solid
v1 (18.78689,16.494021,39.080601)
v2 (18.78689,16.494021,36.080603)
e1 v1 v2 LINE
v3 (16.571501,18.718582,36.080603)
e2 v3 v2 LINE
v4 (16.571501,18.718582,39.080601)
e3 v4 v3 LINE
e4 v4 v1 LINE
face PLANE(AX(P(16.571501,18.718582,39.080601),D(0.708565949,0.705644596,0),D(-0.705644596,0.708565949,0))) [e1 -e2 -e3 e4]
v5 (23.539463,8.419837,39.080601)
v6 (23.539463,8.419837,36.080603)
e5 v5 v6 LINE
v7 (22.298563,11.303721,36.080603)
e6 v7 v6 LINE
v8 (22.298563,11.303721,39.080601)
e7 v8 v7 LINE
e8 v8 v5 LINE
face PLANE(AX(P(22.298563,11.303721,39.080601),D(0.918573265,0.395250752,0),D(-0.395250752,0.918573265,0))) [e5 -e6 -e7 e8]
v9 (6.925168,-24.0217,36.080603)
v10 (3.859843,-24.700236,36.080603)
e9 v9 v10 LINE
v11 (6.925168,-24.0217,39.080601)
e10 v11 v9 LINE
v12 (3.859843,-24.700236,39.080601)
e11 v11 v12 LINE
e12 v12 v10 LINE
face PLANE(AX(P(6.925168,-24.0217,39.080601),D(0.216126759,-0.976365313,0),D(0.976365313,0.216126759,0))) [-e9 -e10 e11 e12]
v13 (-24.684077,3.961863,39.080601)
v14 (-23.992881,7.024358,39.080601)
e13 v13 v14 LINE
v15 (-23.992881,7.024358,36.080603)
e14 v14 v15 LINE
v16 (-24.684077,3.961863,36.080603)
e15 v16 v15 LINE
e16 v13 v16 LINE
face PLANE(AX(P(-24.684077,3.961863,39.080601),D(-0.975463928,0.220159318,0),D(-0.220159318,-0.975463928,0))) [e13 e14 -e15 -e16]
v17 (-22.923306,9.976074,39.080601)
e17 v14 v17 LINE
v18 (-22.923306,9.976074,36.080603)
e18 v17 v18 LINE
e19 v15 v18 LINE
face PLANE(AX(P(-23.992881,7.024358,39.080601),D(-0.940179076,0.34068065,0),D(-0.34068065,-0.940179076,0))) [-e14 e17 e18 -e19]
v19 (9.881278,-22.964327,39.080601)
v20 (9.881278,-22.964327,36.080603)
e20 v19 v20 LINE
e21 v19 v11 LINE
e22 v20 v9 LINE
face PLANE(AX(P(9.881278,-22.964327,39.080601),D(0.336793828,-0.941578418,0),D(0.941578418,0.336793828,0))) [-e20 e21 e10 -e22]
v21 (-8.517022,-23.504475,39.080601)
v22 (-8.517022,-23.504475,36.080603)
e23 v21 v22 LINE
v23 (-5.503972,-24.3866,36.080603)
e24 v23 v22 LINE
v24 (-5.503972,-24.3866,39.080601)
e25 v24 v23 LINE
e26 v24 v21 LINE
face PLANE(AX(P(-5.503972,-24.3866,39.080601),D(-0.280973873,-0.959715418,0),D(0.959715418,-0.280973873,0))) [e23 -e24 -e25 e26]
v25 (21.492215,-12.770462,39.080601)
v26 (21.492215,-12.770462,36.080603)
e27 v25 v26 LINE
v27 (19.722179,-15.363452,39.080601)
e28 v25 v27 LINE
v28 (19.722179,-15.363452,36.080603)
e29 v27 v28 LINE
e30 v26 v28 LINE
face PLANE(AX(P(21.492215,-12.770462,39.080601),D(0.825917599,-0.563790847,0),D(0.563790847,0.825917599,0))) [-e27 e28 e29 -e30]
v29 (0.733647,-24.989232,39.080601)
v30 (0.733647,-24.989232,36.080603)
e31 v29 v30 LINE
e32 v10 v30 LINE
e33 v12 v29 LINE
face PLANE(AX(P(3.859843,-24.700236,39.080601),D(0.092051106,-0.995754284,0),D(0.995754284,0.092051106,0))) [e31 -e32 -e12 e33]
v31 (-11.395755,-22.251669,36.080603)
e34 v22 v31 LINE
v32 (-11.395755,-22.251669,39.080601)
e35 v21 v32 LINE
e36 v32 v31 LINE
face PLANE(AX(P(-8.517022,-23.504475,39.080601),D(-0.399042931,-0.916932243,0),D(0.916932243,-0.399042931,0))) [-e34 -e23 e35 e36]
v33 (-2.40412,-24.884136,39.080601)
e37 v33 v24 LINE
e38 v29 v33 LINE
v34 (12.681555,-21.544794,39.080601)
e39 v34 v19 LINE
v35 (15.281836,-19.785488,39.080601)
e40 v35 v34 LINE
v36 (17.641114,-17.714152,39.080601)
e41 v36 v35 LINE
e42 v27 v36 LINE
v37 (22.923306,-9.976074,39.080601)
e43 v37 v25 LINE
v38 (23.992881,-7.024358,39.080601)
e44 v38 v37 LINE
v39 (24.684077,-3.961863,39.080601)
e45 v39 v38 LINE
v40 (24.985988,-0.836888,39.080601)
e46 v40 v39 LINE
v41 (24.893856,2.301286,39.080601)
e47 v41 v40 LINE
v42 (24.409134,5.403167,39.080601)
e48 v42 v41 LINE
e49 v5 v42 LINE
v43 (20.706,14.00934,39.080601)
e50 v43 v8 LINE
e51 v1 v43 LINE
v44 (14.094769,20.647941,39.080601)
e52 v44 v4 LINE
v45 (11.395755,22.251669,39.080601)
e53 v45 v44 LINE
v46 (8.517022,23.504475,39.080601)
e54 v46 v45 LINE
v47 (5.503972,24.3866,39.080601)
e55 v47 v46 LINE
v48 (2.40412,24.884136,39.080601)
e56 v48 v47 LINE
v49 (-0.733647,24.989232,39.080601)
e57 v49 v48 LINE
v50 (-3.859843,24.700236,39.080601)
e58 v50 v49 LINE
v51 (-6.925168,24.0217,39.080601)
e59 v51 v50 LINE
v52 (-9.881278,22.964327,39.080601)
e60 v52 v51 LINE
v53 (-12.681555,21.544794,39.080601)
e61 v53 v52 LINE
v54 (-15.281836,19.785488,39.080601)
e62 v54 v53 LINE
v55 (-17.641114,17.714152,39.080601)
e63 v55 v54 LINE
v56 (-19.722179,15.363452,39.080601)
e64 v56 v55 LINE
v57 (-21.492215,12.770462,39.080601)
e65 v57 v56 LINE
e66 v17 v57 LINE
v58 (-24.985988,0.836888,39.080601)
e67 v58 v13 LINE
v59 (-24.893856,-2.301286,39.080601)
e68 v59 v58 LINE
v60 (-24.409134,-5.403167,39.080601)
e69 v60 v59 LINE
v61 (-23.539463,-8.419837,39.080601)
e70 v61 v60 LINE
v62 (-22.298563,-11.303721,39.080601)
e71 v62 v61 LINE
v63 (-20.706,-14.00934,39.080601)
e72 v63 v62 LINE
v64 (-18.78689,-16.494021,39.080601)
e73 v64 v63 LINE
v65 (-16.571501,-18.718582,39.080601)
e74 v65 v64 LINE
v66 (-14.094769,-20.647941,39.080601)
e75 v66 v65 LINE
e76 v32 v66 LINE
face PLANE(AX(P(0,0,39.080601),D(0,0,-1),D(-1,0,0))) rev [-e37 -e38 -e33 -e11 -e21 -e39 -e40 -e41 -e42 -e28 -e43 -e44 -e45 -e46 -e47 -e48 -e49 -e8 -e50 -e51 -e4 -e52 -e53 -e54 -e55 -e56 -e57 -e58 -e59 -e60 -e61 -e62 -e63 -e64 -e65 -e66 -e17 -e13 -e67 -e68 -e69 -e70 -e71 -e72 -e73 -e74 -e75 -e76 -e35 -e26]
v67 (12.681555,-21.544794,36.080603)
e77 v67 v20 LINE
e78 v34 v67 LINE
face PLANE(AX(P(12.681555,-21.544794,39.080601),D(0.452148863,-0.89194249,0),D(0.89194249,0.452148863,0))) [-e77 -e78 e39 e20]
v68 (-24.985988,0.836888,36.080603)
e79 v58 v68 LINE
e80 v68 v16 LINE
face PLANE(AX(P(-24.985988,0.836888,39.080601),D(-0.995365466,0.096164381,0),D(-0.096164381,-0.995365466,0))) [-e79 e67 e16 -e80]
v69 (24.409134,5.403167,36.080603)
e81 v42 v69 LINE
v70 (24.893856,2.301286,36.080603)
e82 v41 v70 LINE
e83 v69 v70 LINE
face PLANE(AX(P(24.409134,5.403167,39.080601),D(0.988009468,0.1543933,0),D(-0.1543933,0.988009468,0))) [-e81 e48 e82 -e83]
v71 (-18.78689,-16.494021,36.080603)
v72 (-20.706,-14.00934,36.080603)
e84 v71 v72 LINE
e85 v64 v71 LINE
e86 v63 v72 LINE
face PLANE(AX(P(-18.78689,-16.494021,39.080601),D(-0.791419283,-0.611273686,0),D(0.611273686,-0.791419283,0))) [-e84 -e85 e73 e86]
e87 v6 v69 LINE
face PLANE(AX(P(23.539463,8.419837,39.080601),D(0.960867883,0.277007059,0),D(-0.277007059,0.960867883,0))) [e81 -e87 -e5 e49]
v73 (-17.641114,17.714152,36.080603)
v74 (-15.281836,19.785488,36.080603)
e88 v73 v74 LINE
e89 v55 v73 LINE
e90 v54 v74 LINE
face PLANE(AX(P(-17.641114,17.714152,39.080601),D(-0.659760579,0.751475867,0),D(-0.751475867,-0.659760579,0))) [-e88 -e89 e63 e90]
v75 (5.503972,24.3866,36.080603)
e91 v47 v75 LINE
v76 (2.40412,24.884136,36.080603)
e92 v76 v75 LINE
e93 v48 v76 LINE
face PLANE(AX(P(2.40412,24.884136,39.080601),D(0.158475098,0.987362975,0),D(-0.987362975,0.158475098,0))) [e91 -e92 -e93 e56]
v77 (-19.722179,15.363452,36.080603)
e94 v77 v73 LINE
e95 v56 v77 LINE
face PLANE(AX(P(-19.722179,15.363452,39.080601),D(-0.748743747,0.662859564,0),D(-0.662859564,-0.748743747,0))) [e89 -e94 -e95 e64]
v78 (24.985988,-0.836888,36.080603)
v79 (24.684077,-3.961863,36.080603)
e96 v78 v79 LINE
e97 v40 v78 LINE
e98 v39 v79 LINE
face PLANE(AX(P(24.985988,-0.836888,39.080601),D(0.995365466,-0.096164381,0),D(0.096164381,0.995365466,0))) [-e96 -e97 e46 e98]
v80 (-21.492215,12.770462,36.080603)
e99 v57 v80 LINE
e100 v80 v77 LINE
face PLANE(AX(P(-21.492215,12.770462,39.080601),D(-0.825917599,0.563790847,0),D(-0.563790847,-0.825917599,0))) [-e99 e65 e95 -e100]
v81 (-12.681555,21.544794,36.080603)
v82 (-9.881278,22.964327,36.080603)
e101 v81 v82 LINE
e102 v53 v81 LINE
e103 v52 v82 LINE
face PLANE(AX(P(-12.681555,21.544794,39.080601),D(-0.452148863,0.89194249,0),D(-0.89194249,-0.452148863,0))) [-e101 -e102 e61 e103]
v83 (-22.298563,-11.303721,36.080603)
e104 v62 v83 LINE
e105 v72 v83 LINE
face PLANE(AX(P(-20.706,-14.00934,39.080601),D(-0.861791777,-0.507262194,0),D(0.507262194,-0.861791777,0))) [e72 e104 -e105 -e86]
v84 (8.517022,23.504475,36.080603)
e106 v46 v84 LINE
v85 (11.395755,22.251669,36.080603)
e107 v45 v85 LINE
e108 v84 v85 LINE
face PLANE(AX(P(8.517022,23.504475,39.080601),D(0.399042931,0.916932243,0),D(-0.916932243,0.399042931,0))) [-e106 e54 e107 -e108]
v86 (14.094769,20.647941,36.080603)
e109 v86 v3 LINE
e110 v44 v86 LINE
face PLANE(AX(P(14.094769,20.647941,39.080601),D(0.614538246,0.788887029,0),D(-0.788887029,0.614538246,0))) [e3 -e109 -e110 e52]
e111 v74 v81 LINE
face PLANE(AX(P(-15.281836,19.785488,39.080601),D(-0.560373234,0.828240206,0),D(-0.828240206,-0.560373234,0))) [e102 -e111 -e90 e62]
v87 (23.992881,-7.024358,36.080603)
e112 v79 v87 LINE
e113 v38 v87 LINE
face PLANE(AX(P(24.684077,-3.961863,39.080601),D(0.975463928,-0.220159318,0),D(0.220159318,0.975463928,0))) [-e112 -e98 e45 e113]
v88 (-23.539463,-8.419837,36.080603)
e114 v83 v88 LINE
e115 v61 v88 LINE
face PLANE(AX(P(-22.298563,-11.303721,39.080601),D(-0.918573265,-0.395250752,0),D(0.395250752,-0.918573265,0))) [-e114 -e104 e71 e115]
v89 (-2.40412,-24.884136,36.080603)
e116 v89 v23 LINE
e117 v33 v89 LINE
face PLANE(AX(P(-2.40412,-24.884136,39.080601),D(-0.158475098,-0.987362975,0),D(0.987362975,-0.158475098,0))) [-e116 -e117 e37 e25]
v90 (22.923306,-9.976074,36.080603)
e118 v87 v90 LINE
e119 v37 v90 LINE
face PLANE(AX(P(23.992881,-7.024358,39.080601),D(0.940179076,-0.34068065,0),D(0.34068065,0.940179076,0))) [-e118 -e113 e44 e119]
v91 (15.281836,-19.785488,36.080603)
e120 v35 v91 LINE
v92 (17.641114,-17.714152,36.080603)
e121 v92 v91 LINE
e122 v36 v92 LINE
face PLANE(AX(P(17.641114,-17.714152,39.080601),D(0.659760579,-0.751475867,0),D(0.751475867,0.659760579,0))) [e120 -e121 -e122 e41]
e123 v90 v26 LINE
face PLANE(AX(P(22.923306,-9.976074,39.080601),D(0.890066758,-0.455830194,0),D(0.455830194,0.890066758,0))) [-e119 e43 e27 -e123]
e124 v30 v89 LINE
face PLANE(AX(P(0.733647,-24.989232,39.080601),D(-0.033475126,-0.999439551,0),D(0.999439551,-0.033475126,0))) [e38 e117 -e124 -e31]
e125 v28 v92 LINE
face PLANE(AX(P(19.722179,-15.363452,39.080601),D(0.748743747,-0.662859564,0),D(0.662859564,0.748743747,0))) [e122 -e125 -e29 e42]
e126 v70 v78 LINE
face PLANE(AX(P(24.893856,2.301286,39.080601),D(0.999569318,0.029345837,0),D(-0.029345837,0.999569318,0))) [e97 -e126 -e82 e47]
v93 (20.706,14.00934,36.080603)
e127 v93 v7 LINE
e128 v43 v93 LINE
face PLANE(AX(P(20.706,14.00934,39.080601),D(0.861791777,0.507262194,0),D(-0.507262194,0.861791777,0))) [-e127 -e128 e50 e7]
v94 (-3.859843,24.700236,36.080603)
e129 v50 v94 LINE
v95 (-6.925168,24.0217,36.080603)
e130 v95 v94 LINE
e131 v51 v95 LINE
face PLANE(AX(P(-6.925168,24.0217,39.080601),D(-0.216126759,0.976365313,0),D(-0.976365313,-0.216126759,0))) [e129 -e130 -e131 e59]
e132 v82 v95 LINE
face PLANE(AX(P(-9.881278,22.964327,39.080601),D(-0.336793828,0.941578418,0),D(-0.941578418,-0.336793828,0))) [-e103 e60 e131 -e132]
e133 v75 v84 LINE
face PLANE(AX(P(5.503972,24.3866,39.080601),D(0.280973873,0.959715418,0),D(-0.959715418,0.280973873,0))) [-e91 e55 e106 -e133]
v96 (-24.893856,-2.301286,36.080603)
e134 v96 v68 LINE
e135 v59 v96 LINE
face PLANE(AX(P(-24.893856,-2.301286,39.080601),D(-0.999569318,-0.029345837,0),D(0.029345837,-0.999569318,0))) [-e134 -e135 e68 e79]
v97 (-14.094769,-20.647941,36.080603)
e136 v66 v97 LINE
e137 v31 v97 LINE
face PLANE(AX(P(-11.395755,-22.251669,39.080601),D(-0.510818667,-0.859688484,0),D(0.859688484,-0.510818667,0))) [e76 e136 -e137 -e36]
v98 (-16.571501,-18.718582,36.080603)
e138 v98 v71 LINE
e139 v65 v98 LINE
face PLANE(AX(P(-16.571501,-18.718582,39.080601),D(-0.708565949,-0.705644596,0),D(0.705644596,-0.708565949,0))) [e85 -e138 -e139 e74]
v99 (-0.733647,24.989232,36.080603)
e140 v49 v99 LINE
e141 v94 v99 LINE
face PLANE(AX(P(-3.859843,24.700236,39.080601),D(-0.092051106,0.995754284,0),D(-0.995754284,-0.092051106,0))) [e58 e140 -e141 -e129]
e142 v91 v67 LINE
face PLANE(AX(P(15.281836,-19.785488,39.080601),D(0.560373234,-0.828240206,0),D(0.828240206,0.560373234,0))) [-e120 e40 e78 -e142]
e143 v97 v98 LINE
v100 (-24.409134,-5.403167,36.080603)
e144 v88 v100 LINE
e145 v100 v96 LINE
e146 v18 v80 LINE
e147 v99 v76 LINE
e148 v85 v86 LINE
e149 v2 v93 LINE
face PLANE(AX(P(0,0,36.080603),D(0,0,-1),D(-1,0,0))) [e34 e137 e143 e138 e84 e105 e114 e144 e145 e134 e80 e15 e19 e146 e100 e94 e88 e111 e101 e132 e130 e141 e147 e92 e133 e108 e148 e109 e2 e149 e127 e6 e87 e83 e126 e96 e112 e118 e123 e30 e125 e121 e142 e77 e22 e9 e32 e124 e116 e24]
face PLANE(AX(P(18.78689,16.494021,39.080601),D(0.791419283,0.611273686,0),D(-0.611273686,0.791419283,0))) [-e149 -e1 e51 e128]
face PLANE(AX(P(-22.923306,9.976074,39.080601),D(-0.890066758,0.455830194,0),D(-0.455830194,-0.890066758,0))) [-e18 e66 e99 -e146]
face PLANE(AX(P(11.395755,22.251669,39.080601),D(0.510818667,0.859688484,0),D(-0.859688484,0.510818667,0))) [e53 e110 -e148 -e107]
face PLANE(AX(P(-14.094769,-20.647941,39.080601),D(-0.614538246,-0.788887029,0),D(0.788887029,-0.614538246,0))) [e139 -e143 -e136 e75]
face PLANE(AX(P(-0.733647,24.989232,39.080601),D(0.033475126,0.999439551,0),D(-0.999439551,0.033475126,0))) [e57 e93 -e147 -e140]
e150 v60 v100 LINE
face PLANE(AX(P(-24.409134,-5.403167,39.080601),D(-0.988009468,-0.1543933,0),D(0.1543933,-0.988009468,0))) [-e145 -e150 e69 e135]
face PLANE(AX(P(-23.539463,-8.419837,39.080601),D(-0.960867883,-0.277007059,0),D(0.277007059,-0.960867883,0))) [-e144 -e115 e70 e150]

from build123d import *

# Parameters (mm, degrees)
BOSS_EXTRUDE1_DEPTH = 2.999998629


with BuildPart() as part:
    # Sketch1 → Boss-Extrude1 (new body)
    with BuildSketch(Plane(origin=(0, 0, 36.080602556), x_dir=(-1, 0, 0), z_dir=(0, 0, -1))):
        Polygon((24.985987693, 0.836887804), (24.684077129, 3.961863462), (23.992881179, 7.024358027), (22.923305631, 9.9760741), (21.492214873, 12.77046185), (19.722178578, 15.363452025), (17.641114071, 17.714152113), (15.281835571, 19.785488024), (12.681555003, 21.544793621), (9.8812785, 22.964326665), (6.925167516, 24.021700025), (3.85984336, 24.700235575), (0.733646855, 24.989232421), (-2.404119587, 24.884136394), (-5.503971595, 24.38659966), (-8.517022245, 23.504475132), (-11.395755224, 22.251669317), (-14.094769023, 20.647941157), (-16.57150127, 18.718581647), (-18.786890432, 16.49402082), (-20.705999807, 14.009339735), (-22.298563272, 11.303720996), (-23.539463058, 8.419836871), (-24.409133941, 5.403167102), (-24.893855676, 2.301285975), (-24.985987693, -0.836887804), (-24.684077129, -3.961863462), (-23.992881179, -7.024358027), (-22.923305631, -9.9760741), (-21.492214873, -12.77046185), (-19.722178578, -15.363452025), (-17.641114071, -17.714152113), (-15.281835571, -19.785488024), (-12.681555003, -21.544793621), (-9.8812785, -22.964326665), (-6.925167516, -24.021700025), (-3.85984336, -24.700235575), (-0.733646855, -24.989232421), (2.404119587, -24.884136394), (5.503971595, -24.38659966), (8.517022245, -23.504475132), (11.395755224, -22.251669317), (14.094769023, -20.647941157), (16.57150127, -18.718581647), (18.786890432, -16.49402082), (20.705999807, -14.009339735), (22.298563272, -11.303720996), (23.539463058, -8.419836871), (24.409133941, -5.403167102), (24.893855676, -2.301285975), align=None)
    extrude(amount=-BOSS_EXTRUDE1_DEPTH)


solid = part.part
